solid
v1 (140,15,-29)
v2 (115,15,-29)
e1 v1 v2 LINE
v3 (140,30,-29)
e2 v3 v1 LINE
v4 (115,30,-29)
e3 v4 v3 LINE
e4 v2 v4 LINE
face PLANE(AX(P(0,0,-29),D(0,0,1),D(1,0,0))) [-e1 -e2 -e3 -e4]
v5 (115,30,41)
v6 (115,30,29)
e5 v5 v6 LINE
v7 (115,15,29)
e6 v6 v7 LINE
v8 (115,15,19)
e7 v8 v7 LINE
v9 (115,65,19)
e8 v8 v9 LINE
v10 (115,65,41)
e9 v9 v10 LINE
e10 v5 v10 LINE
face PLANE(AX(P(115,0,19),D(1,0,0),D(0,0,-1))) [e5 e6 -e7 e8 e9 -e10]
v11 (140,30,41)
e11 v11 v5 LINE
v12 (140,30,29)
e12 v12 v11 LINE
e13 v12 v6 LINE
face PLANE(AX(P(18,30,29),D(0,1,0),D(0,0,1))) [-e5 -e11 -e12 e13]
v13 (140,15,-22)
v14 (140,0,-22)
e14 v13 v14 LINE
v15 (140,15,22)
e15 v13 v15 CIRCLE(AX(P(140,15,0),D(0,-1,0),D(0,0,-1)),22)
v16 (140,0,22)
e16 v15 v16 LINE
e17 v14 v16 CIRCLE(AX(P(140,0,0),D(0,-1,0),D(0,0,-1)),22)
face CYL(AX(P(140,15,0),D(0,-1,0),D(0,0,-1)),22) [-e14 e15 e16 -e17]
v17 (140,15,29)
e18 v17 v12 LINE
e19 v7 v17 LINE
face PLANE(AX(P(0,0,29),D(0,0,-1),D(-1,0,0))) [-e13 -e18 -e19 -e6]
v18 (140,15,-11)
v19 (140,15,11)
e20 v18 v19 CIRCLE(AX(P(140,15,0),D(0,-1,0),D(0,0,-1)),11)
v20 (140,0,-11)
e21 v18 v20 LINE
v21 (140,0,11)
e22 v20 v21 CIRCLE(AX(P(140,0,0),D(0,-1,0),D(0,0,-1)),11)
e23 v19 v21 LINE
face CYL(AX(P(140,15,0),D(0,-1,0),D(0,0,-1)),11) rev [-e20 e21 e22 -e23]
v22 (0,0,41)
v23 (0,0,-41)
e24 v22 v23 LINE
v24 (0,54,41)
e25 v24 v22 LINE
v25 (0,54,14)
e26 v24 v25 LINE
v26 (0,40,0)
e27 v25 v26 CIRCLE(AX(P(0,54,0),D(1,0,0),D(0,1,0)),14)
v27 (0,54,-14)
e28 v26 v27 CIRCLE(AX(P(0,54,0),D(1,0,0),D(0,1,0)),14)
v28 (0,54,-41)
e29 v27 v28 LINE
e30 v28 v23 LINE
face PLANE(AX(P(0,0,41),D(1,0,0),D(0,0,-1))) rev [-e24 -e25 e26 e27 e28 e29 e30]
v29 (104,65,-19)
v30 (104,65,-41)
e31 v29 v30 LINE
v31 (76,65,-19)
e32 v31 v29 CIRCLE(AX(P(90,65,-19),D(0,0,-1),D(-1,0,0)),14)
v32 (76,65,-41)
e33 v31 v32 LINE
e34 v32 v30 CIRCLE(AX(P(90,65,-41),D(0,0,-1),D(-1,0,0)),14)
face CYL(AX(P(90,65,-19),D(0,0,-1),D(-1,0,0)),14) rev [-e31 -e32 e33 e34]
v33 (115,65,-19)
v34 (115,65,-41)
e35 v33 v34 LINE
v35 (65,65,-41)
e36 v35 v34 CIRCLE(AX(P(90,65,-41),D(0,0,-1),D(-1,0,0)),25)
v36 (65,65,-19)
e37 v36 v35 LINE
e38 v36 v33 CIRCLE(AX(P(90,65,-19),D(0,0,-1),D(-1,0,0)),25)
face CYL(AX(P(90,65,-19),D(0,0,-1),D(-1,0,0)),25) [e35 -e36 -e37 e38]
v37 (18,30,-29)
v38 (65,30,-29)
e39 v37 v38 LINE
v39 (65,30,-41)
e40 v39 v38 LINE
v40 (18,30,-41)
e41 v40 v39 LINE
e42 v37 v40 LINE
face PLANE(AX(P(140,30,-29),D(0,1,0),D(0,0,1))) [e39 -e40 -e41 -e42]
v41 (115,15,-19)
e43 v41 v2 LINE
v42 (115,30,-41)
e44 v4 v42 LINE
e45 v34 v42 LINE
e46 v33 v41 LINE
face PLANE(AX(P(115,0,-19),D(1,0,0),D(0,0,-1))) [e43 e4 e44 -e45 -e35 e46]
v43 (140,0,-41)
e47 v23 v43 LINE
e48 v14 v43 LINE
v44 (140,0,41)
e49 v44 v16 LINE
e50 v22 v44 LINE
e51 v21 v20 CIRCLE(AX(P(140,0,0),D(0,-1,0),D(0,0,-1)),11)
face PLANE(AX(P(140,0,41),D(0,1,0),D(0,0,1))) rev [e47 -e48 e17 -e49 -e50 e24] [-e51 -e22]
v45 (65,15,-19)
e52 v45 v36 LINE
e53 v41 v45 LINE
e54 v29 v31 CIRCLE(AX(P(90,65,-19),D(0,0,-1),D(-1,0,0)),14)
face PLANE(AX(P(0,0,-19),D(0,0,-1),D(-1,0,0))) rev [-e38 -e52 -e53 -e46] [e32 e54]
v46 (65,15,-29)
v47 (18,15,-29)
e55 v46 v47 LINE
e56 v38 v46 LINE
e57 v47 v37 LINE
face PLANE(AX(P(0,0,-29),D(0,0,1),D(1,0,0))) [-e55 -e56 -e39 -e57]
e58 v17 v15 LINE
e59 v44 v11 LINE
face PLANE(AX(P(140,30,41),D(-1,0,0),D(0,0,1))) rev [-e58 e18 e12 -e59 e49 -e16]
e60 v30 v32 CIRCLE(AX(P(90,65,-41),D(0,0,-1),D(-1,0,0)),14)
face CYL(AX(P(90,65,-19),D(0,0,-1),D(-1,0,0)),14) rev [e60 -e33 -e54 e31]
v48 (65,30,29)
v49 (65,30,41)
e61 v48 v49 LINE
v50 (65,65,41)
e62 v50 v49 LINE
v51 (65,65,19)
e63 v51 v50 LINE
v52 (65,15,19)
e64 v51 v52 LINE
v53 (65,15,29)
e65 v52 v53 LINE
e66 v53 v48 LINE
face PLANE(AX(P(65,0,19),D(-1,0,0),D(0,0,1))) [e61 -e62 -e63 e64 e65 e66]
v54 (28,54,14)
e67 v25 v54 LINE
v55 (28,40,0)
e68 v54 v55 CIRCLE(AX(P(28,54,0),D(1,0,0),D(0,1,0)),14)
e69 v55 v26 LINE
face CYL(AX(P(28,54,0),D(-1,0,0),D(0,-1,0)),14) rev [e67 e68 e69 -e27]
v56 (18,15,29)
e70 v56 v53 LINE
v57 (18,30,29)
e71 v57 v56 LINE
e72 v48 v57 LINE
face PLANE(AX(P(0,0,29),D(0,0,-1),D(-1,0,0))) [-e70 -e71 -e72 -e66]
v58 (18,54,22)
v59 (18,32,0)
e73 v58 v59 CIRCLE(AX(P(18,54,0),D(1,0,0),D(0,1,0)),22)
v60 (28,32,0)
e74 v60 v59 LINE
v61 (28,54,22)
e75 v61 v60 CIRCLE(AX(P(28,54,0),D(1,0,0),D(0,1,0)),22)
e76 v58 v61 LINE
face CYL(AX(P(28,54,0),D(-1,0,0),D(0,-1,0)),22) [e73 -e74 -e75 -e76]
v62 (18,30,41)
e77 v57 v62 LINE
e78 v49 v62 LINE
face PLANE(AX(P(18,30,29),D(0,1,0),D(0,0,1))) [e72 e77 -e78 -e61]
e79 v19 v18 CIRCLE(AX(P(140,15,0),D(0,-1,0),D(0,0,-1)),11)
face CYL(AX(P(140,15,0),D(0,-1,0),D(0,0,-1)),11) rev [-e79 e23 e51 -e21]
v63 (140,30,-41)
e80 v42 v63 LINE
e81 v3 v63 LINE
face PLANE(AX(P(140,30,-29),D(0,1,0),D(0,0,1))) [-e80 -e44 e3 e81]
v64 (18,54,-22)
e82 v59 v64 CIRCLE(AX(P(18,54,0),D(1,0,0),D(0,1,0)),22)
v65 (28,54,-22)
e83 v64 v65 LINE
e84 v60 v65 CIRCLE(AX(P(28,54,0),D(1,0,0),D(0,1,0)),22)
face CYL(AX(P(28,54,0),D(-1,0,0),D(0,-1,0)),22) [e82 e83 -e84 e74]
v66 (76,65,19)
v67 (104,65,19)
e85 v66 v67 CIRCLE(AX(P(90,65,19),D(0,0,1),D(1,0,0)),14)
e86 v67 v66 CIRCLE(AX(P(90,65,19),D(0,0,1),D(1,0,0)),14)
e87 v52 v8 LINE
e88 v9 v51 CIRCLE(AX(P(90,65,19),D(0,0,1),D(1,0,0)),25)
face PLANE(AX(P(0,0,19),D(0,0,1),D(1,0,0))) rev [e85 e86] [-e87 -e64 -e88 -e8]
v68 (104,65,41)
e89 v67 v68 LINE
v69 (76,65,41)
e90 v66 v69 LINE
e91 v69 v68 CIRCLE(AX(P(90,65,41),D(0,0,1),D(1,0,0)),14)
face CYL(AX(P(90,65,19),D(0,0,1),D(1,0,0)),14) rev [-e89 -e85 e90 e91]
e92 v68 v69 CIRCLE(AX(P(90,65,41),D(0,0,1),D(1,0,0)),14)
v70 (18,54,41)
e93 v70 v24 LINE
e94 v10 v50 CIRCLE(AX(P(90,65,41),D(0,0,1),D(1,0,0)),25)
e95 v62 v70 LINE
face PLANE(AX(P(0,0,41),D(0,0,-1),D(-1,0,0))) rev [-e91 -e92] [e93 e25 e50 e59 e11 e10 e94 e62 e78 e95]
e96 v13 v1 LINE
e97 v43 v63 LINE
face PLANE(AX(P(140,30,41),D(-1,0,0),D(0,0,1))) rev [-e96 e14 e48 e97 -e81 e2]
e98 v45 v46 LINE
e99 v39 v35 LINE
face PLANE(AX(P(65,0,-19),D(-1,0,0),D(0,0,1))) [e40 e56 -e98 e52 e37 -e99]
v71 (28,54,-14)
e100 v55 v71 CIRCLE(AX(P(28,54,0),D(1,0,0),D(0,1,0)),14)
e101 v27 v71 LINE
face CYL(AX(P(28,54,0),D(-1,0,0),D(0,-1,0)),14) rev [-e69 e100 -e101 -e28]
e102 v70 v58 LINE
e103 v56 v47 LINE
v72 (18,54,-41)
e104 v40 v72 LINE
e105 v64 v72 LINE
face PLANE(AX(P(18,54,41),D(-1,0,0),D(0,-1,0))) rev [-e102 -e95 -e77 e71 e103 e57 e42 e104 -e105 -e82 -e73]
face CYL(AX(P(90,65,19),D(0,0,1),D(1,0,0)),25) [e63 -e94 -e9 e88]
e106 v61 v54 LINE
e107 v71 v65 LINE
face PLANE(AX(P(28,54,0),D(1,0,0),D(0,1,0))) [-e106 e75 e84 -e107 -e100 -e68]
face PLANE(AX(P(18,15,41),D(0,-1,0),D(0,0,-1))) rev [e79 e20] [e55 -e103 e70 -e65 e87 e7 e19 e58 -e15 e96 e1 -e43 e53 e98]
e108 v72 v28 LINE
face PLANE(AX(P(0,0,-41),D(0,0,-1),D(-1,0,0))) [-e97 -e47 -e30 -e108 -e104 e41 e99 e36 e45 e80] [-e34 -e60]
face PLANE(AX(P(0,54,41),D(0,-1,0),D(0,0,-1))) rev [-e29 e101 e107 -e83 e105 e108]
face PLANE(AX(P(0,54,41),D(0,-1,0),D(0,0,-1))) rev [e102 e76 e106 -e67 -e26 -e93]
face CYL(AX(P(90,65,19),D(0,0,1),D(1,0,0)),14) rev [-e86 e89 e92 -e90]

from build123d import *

# Parameters (mm, degrees)
BASE_BLOCK_DEPTH         = 41
CHANNEL_POCKET_SKETCH_W  = 82
CHANNEL_POCKET_SKETCH_H  = 15
CHANNEL_POCKET_DEPTH     = 122
RAIL_PAD_A_SKETCH_W      = 122
RAIL_PAD_A_SKETCH_H      = 15
RAIL_PAD_A_DEPTH         = 12
RAIL_PAD_B_SKETCH_W      = 122
RAIL_PAD_B_SKETCH_H      = 15
RAIL_PAD_B_DEPTH         = 12
CLEVIS_EAR_1_SKETCH_R    = 14
CLEVIS_EAR_1_DEPTH       = 22
CLEVIS_START             = -22
CLEVIS_EAR_2_SKETCH_W    = 50
CLEVIS_EAR_2_SKETCH_H    = 15
CLEVIS_EAR_2_DEPTH       = 22
CLEVIS_PIN_HOLE_SKETCH_R = 14
CLEVIS_PIN_HOLE_28_DEPTH = 22
SADDLE_BOSS_SKETCH_R     = 22
SADDLE_BOSS_SKETCH_R_2   = 14
SADDLE_BOSS_DEPTH        = 10
SADDLE_START             = -10
SADDLE_TRIM_CUT_DEPTH    = 10
SADDLE_START_2           = -28
SADDLE_BORE_SKETCH_R     = 14
SADDLE_HALF_BORE_DEPTH   = 28
END_LUG_DEPTH            = 15
END_LUG_HOLE_SKETCH_R    = 11
END_LUG_HOLE_22_DEPTH    = 15


with BuildPart() as part:
    # Base Profile Sketch → Base Block (new, symmetric)
    with BuildSketch(Plane.XY):
        Polygon((0, 0), (0, 54), (18, 54), (18, 30), (140, 30), (140, 0), align=None)
    extrude(amount=BASE_BLOCK_DEPTH, both=True)

    # Channel Pocket Sketch → Channel Pocket (cut)
    with BuildSketch(Plane(origin=(140, 0, 0), x_dir=(0, 0, -1), z_dir=(1, 0, 0))):
        with Locations((0, 22.5)):
            Rectangle(CHANNEL_POCKET_SKETCH_W, CHANNEL_POCKET_SKETCH_H)
    extrude(amount=-CHANNEL_POCKET_DEPTH, mode=Mode.SUBTRACT)

    # Rail Pad A Sketch → Rail Pad A (add)
    with BuildSketch(Plane.XY.offset(41)):
        with Locations((79, 22.5)):
            Rectangle(RAIL_PAD_A_SKETCH_W, RAIL_PAD_A_SKETCH_H)
    extrude(amount=-RAIL_PAD_A_DEPTH)

    # Rail Pad B Sketch → Rail Pad B (add)
    with BuildSketch(Plane(origin=(0, 0, -41), x_dir=(-1, 0, 0), z_dir=(0, 0, -1))):
        with Locations((-79, 22.5)):
            Rectangle(RAIL_PAD_B_SKETCH_W, RAIL_PAD_B_SKETCH_H)
    extrude(amount=-RAIL_PAD_B_DEPTH)

    # Clevis Ear 1 Sketch → Clevis Ear 1 (add)
    with BuildSketch(Plane.XY.offset(41)):
        with BuildLine():
            Line((65, 65), (65, 15))
            Line((65, 15), (115, 15))
            Line((115, 15), (115, 65))
            ThreePointArc((115, 65), (90, 90), (65, 65))
        make_face()
        with Locations((90, 65)):
            Circle(CLEVIS_EAR_1_SKETCH_R, mode=Mode.SUBTRACT)
    extrude(amount=-CLEVIS_EAR_1_DEPTH)

    # Clevis Ear 2 Sketch → Clevis Ear 2 (add)
    with BuildSketch(Plane(origin=(0, 0, -41), x_dir=(-1, 0, 0), z_dir=(0, 0, -1)).offset(CLEVIS_START)):
        with BuildLine():
            Line((-115, 30), (-65, 30))
            Line((-65, 30), (-65, 65))
            ThreePointArc((-65, 65), (-90, 90), (-115, 65))
            Line((-115, 65), (-115, 30))
        make_face()
        with Locations((-90, 22.5)):
            Rectangle(CLEVIS_EAR_2_SKETCH_W, CLEVIS_EAR_2_SKETCH_H)
    extrude(amount=CLEVIS_EAR_2_DEPTH)

    # Clevis Pin Hole Sketch → Clevis Pin Hole Ø28 (cut)
    with BuildSketch(Plane(origin=(0, 0, -41), x_dir=(-1, 0, 0), z_dir=(0, 0, -1)).offset(CLEVIS_START)):
        with Locations(Location((-90, 65, 0), (0, 0, 180))):
            Circle(CLEVIS_PIN_HOLE_SKETCH_R)
    extrude(amount=CLEVIS_PIN_HOLE_28_DEPTH, mode=Mode.SUBTRACT)

    # Saddle Boss Sketch → Saddle Boss (add)
    with BuildSketch(Plane(origin=(18, 0, 0), x_dir=(0, 0, -1), z_dir=(1, 0, 0))):
        with Locations((0, 54)):
            Circle(SADDLE_BOSS_SKETCH_R)
        with Locations(Location((0, 54, 0), (0, 0, 180))):
            Circle(SADDLE_BOSS_SKETCH_R_2, mode=Mode.SUBTRACT)
    extrude(amount=SADDLE_BOSS_DEPTH)

    # Saddle Trim Sketch → Saddle Trim Cut (cut)
    with BuildSketch(Plane(origin=(28, 0, 0), x_dir=(0, 0, -1), z_dir=(1, 0, 0)).offset(SADDLE_START)):
        with BuildLine():
            ThreePointArc((22, 54), (0, 76), (-22, 54))
            Line((-22, 54), (-14, 54))
            ThreePointArc((-14, 54), (0, 68), (14, 54))
            Line((14, 54), (22, 54))
        make_face()
    extrude(amount=SADDLE_TRIM_CUT_DEPTH, mode=Mode.SUBTRACT)

    # Saddle Bore Sketch → Saddle Half Bore (cut)
    with BuildSketch(Plane(origin=(28, 0, 0), x_dir=(0, 0, -1), z_dir=(1, 0, 0)).offset(SADDLE_START_2)):
        with Locations((0, 54)):
            Circle(SADDLE_BORE_SKETCH_R)
    extrude(amount=SADDLE_HALF_BORE_DEPTH, mode=Mode.SUBTRACT)

    # End Lug Sketch → End Lug (add)
    with BuildSketch(Plane.XZ):
        with BuildLine():
            Line((140, 22), (140, -22))
            ThreePointArc((140, -22), (162, 0), (140, 22))
        make_face()
    extrude(amount=-END_LUG_DEPTH)

    # End Lug Hole Sketch → End Lug Hole Ø22 (cut)
    with BuildSketch(Plane.XZ):
        with Locations(Location((140, 0, 0), (0, 0, 270))):
            Circle(END_LUG_HOLE_SKETCH_R)
    extrude(amount=-END_LUG_HOLE_22_DEPTH, mode=Mode.SUBTRACT)


solid = part.part
